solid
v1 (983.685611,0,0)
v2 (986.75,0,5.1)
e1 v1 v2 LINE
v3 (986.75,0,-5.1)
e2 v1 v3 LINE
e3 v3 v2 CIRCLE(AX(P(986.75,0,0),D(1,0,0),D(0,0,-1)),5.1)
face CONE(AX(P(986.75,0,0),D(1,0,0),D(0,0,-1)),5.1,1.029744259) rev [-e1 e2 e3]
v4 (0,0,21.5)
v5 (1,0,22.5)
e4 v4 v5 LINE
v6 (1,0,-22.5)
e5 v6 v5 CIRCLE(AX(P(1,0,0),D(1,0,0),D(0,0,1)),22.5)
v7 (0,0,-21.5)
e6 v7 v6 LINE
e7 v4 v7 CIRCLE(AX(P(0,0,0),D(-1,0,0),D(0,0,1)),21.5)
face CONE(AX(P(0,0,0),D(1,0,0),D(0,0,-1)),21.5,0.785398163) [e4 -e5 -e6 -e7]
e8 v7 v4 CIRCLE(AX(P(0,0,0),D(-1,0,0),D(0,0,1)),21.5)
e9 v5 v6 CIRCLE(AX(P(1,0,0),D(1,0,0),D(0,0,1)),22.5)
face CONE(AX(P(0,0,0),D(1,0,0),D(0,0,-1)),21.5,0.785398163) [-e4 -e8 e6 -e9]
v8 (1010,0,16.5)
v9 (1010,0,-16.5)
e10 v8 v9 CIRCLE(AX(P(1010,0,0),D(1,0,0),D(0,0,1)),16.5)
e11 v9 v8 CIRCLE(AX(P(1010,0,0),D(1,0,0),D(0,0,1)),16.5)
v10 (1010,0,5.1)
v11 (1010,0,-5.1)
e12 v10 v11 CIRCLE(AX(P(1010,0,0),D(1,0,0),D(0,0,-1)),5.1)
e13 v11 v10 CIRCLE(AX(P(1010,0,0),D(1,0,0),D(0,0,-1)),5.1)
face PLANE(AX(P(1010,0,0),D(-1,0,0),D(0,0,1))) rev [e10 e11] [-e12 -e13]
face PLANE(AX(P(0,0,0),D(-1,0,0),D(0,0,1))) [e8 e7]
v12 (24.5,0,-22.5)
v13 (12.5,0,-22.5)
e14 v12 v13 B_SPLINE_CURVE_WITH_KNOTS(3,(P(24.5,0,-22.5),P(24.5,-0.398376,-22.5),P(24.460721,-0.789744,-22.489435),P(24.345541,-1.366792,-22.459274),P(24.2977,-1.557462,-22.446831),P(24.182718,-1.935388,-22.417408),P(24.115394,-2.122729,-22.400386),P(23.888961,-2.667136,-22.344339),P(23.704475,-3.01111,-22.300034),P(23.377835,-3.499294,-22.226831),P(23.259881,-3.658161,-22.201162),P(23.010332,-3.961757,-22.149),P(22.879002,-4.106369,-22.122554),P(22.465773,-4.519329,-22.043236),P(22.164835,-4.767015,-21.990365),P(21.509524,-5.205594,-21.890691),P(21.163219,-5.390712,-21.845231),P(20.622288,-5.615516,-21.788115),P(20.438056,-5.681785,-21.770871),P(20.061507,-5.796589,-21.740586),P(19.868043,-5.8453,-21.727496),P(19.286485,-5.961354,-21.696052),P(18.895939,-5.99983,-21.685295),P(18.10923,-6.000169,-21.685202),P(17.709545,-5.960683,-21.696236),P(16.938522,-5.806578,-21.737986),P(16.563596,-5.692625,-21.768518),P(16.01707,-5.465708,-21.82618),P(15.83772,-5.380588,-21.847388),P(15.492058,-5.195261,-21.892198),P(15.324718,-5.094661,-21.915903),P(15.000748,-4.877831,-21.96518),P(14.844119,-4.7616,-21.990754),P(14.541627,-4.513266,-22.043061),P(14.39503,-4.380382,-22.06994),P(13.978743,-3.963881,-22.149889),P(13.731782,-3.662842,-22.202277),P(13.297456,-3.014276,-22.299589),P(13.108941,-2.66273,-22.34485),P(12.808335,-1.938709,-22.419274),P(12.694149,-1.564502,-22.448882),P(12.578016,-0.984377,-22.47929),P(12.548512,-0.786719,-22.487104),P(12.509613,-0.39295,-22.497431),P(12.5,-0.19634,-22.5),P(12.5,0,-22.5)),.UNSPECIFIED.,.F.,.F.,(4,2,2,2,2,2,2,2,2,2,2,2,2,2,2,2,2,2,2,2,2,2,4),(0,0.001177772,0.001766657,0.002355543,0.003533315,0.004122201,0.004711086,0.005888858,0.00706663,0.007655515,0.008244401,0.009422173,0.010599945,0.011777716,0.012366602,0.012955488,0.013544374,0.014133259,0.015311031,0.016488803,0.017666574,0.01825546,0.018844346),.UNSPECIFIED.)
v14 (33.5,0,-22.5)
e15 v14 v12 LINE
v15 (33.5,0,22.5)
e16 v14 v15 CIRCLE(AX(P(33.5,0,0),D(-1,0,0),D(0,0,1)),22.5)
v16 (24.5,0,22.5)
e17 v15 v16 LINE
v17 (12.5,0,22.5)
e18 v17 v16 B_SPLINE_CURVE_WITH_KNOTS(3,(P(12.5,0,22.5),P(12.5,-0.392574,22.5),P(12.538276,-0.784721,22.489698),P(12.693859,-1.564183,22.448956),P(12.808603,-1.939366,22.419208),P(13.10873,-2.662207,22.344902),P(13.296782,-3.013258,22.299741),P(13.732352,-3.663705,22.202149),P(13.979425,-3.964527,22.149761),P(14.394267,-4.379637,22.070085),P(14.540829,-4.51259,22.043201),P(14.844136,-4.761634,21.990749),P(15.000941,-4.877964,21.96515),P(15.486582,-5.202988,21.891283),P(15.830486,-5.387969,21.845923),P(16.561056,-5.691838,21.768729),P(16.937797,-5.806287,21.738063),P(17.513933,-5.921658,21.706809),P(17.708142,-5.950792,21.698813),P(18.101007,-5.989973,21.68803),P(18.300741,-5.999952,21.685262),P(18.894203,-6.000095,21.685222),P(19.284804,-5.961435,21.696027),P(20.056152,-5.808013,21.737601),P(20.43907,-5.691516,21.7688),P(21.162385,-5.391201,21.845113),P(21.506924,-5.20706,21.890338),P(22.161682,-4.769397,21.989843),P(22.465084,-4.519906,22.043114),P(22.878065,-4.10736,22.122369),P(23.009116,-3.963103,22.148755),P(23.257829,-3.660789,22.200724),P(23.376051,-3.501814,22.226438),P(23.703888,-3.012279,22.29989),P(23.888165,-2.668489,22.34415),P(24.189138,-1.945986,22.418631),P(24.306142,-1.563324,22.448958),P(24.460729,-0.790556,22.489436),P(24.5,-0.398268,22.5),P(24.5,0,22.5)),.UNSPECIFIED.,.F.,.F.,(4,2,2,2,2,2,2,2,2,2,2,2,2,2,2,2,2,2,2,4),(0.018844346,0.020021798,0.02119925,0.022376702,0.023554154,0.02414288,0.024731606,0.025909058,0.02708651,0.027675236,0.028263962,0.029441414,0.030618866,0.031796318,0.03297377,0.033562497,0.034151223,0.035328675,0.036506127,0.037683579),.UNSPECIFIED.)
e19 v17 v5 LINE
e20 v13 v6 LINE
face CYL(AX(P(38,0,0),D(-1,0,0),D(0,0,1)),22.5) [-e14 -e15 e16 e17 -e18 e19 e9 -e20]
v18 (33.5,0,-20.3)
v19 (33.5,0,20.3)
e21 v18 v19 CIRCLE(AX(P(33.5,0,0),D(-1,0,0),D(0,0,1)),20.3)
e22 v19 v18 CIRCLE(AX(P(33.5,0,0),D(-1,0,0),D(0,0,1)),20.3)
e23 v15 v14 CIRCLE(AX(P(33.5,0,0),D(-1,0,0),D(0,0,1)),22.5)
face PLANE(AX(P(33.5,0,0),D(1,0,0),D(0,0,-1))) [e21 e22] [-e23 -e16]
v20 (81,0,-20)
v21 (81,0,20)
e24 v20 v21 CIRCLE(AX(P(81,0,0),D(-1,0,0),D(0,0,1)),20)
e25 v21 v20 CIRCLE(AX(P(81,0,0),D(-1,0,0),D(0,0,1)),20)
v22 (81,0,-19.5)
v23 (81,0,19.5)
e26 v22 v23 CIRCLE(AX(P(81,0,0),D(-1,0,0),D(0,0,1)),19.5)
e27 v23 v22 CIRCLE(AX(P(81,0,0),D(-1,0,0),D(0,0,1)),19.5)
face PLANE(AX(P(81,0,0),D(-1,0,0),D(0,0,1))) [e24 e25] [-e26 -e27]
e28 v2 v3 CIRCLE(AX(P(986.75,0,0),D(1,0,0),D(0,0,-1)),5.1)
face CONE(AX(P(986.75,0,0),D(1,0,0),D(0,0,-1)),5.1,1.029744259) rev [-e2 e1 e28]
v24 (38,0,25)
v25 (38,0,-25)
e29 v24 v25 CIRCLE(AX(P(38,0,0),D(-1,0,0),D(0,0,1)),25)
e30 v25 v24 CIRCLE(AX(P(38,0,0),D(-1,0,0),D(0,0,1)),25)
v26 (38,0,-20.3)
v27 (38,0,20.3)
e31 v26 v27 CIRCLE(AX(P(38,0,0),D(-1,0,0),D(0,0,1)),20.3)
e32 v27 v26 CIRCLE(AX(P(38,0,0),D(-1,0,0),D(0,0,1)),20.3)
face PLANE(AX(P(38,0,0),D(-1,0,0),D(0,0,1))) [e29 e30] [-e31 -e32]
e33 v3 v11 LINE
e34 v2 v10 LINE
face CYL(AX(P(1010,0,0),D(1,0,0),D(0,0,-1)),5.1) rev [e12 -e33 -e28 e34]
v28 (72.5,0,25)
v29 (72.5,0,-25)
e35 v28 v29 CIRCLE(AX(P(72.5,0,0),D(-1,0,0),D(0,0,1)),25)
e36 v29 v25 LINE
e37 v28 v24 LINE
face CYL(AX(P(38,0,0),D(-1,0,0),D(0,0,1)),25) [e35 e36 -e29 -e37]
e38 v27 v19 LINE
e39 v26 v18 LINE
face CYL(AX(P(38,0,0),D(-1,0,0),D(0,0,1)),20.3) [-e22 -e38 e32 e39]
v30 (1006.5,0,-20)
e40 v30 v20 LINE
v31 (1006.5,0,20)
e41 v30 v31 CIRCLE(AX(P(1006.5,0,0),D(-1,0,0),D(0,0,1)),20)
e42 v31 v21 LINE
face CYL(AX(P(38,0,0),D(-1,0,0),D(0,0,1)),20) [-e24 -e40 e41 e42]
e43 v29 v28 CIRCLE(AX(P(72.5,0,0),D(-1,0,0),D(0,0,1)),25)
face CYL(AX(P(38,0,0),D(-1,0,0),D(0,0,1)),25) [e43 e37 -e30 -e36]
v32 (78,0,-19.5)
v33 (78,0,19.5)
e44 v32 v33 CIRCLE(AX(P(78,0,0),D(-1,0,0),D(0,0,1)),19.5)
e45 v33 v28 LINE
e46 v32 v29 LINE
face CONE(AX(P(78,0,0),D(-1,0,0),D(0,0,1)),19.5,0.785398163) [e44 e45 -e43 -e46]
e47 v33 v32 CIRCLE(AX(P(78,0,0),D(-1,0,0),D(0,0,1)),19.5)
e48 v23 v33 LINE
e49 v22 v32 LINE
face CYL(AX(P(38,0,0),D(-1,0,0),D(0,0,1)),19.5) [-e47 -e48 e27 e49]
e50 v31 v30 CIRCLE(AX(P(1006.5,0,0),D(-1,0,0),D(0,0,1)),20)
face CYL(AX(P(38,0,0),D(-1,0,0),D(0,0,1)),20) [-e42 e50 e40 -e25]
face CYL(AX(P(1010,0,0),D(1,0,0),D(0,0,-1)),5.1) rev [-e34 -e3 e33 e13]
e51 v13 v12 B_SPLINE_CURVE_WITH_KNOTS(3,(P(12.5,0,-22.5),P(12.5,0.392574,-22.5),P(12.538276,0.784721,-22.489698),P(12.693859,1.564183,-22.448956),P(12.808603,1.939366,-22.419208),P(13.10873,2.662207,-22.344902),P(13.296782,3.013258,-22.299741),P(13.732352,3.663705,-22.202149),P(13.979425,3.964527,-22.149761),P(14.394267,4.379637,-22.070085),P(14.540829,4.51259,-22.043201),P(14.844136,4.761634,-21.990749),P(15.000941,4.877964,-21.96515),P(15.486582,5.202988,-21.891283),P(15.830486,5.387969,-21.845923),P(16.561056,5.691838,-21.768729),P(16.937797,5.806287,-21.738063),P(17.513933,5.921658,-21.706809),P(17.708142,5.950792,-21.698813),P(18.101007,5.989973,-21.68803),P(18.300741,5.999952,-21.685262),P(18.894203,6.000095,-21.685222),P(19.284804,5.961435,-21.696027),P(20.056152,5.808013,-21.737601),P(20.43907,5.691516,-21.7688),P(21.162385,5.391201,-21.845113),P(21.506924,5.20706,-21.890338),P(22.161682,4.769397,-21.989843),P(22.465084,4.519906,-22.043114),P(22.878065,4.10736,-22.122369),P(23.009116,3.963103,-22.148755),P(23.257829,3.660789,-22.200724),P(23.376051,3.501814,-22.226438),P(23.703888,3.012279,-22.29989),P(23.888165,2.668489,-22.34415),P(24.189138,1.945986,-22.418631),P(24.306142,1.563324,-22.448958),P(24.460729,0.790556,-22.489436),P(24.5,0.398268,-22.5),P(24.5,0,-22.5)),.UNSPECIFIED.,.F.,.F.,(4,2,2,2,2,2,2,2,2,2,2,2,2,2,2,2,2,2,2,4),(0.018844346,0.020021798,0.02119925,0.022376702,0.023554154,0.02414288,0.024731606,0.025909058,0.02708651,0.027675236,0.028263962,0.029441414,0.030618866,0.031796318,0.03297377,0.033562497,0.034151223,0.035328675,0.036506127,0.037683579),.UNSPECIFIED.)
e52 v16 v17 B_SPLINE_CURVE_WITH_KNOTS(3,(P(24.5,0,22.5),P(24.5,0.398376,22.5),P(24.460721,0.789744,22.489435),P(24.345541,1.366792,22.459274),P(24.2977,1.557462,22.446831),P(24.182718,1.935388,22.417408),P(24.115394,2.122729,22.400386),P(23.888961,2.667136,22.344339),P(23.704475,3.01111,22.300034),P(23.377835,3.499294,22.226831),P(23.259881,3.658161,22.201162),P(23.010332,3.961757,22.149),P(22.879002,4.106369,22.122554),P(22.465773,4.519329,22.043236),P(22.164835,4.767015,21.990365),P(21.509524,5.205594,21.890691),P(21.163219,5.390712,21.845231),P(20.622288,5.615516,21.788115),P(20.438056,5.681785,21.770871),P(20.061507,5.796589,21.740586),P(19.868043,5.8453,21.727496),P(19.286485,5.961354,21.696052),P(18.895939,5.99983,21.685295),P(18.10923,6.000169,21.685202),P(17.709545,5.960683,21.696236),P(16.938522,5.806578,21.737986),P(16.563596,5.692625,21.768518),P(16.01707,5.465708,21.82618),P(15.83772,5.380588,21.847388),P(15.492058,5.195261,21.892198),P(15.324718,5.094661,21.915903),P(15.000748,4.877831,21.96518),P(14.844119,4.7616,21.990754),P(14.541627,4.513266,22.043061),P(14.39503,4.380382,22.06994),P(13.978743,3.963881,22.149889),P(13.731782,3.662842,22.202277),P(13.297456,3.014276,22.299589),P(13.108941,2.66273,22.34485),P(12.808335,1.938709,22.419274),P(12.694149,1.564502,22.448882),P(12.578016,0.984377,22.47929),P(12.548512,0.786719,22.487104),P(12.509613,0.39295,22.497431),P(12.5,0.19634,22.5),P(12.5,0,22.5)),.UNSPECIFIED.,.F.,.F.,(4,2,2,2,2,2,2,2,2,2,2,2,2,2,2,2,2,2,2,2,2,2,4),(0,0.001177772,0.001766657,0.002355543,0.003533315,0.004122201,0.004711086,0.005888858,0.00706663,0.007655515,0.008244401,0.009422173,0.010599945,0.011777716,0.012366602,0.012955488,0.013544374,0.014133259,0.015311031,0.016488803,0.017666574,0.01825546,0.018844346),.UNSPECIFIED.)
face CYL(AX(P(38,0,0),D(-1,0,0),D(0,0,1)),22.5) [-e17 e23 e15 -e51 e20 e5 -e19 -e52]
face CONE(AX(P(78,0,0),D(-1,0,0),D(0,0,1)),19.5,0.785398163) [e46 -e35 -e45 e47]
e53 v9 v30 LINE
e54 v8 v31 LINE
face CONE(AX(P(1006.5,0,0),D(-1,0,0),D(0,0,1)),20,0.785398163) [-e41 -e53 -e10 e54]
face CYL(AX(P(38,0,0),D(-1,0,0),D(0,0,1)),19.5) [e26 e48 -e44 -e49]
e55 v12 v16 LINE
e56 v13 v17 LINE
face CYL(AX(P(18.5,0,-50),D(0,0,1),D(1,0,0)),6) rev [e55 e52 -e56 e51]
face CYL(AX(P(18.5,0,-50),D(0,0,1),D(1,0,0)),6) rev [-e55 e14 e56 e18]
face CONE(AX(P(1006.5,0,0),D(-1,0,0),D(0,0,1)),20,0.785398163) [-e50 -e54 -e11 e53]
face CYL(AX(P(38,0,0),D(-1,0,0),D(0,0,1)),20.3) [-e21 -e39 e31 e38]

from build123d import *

# Parameters (mm, degrees)
CHAMFER1_SIZE          = 3.5
CHAMFER2_SIZE          = 1
SKETCH2_R              = 6
CUT_EXTRUDE1_DEPTH     = 50
M12_TAPPED_HOLE1_D     = 10.2
M12_TAPPED_HOLE1_DEPTH = 23.25
M12_TAPPED_HOLE1_TIP   = 3.064389157


with BuildPart() as part:
    # Sketch1 → Revolve1 (revolve)
    with BuildSketch(Plane.XY, mode=Mode.PRIVATE) as revolve1_sk:
        Polygon((81, 19.5), (78, 19.5), (72.5, 25), (38, 25), (38, 22.5), (38, 20.3), (33.5, 20.3), (33.5, 22.5), (0, 22.5), (0, 0), (38, 0), (78, 0), (81, 0), (1010, 0), (1010, 20), (81, 20), align=None)
    revolve(revolve1_sk.sketch.rotate(Axis((38, 0, 0), (1, 0, 0)), 90), axis=Axis((38, 0, 0), (1, 0, 0)))

    # Chamfer1
    chamfer1_edges = [part.edges().sort_by_distance(p)[0] for p in [
        (1010, 0, -20),
    ]]
    chamfer(chamfer1_edges, length=CHAMFER1_SIZE)

    # Chamfer2
    chamfer2_edges = [part.edges().sort_by_distance(p)[0] for p in [
        (0, 0, -22.5),
    ]]
    chamfer(chamfer2_edges, length=CHAMFER2_SIZE)

    # Sketch2 → Cut-Extrude1 (cut, symmetric)
    with BuildSketch(Plane.XY):
        with Locations((18.5, 0)):
            Circle(SKETCH2_R)
    extrude(amount=CUT_EXTRUDE1_DEPTH, both=True, mode=Mode.SUBTRACT)

    # M12 Tapped Hole1
    with Locations(Plane(origin=(1010, 0, 0), x_dir=(0, 0, -1), z_dir=(1, 0, 0))):
        with Locations((0, 0)):
            Hole(M12_TAPPED_HOLE1_D / 2, depth=M12_TAPPED_HOLE1_DEPTH)
            with Locations((0, 0, -(M12_TAPPED_HOLE1_DEPTH + M12_TAPPED_HOLE1_TIP / 2))):  # 118° drill point
                Cone(0, M12_TAPPED_HOLE1_D / 2, M12_TAPPED_HOLE1_TIP, mode=Mode.SUBTRACT)


solid = part.part
